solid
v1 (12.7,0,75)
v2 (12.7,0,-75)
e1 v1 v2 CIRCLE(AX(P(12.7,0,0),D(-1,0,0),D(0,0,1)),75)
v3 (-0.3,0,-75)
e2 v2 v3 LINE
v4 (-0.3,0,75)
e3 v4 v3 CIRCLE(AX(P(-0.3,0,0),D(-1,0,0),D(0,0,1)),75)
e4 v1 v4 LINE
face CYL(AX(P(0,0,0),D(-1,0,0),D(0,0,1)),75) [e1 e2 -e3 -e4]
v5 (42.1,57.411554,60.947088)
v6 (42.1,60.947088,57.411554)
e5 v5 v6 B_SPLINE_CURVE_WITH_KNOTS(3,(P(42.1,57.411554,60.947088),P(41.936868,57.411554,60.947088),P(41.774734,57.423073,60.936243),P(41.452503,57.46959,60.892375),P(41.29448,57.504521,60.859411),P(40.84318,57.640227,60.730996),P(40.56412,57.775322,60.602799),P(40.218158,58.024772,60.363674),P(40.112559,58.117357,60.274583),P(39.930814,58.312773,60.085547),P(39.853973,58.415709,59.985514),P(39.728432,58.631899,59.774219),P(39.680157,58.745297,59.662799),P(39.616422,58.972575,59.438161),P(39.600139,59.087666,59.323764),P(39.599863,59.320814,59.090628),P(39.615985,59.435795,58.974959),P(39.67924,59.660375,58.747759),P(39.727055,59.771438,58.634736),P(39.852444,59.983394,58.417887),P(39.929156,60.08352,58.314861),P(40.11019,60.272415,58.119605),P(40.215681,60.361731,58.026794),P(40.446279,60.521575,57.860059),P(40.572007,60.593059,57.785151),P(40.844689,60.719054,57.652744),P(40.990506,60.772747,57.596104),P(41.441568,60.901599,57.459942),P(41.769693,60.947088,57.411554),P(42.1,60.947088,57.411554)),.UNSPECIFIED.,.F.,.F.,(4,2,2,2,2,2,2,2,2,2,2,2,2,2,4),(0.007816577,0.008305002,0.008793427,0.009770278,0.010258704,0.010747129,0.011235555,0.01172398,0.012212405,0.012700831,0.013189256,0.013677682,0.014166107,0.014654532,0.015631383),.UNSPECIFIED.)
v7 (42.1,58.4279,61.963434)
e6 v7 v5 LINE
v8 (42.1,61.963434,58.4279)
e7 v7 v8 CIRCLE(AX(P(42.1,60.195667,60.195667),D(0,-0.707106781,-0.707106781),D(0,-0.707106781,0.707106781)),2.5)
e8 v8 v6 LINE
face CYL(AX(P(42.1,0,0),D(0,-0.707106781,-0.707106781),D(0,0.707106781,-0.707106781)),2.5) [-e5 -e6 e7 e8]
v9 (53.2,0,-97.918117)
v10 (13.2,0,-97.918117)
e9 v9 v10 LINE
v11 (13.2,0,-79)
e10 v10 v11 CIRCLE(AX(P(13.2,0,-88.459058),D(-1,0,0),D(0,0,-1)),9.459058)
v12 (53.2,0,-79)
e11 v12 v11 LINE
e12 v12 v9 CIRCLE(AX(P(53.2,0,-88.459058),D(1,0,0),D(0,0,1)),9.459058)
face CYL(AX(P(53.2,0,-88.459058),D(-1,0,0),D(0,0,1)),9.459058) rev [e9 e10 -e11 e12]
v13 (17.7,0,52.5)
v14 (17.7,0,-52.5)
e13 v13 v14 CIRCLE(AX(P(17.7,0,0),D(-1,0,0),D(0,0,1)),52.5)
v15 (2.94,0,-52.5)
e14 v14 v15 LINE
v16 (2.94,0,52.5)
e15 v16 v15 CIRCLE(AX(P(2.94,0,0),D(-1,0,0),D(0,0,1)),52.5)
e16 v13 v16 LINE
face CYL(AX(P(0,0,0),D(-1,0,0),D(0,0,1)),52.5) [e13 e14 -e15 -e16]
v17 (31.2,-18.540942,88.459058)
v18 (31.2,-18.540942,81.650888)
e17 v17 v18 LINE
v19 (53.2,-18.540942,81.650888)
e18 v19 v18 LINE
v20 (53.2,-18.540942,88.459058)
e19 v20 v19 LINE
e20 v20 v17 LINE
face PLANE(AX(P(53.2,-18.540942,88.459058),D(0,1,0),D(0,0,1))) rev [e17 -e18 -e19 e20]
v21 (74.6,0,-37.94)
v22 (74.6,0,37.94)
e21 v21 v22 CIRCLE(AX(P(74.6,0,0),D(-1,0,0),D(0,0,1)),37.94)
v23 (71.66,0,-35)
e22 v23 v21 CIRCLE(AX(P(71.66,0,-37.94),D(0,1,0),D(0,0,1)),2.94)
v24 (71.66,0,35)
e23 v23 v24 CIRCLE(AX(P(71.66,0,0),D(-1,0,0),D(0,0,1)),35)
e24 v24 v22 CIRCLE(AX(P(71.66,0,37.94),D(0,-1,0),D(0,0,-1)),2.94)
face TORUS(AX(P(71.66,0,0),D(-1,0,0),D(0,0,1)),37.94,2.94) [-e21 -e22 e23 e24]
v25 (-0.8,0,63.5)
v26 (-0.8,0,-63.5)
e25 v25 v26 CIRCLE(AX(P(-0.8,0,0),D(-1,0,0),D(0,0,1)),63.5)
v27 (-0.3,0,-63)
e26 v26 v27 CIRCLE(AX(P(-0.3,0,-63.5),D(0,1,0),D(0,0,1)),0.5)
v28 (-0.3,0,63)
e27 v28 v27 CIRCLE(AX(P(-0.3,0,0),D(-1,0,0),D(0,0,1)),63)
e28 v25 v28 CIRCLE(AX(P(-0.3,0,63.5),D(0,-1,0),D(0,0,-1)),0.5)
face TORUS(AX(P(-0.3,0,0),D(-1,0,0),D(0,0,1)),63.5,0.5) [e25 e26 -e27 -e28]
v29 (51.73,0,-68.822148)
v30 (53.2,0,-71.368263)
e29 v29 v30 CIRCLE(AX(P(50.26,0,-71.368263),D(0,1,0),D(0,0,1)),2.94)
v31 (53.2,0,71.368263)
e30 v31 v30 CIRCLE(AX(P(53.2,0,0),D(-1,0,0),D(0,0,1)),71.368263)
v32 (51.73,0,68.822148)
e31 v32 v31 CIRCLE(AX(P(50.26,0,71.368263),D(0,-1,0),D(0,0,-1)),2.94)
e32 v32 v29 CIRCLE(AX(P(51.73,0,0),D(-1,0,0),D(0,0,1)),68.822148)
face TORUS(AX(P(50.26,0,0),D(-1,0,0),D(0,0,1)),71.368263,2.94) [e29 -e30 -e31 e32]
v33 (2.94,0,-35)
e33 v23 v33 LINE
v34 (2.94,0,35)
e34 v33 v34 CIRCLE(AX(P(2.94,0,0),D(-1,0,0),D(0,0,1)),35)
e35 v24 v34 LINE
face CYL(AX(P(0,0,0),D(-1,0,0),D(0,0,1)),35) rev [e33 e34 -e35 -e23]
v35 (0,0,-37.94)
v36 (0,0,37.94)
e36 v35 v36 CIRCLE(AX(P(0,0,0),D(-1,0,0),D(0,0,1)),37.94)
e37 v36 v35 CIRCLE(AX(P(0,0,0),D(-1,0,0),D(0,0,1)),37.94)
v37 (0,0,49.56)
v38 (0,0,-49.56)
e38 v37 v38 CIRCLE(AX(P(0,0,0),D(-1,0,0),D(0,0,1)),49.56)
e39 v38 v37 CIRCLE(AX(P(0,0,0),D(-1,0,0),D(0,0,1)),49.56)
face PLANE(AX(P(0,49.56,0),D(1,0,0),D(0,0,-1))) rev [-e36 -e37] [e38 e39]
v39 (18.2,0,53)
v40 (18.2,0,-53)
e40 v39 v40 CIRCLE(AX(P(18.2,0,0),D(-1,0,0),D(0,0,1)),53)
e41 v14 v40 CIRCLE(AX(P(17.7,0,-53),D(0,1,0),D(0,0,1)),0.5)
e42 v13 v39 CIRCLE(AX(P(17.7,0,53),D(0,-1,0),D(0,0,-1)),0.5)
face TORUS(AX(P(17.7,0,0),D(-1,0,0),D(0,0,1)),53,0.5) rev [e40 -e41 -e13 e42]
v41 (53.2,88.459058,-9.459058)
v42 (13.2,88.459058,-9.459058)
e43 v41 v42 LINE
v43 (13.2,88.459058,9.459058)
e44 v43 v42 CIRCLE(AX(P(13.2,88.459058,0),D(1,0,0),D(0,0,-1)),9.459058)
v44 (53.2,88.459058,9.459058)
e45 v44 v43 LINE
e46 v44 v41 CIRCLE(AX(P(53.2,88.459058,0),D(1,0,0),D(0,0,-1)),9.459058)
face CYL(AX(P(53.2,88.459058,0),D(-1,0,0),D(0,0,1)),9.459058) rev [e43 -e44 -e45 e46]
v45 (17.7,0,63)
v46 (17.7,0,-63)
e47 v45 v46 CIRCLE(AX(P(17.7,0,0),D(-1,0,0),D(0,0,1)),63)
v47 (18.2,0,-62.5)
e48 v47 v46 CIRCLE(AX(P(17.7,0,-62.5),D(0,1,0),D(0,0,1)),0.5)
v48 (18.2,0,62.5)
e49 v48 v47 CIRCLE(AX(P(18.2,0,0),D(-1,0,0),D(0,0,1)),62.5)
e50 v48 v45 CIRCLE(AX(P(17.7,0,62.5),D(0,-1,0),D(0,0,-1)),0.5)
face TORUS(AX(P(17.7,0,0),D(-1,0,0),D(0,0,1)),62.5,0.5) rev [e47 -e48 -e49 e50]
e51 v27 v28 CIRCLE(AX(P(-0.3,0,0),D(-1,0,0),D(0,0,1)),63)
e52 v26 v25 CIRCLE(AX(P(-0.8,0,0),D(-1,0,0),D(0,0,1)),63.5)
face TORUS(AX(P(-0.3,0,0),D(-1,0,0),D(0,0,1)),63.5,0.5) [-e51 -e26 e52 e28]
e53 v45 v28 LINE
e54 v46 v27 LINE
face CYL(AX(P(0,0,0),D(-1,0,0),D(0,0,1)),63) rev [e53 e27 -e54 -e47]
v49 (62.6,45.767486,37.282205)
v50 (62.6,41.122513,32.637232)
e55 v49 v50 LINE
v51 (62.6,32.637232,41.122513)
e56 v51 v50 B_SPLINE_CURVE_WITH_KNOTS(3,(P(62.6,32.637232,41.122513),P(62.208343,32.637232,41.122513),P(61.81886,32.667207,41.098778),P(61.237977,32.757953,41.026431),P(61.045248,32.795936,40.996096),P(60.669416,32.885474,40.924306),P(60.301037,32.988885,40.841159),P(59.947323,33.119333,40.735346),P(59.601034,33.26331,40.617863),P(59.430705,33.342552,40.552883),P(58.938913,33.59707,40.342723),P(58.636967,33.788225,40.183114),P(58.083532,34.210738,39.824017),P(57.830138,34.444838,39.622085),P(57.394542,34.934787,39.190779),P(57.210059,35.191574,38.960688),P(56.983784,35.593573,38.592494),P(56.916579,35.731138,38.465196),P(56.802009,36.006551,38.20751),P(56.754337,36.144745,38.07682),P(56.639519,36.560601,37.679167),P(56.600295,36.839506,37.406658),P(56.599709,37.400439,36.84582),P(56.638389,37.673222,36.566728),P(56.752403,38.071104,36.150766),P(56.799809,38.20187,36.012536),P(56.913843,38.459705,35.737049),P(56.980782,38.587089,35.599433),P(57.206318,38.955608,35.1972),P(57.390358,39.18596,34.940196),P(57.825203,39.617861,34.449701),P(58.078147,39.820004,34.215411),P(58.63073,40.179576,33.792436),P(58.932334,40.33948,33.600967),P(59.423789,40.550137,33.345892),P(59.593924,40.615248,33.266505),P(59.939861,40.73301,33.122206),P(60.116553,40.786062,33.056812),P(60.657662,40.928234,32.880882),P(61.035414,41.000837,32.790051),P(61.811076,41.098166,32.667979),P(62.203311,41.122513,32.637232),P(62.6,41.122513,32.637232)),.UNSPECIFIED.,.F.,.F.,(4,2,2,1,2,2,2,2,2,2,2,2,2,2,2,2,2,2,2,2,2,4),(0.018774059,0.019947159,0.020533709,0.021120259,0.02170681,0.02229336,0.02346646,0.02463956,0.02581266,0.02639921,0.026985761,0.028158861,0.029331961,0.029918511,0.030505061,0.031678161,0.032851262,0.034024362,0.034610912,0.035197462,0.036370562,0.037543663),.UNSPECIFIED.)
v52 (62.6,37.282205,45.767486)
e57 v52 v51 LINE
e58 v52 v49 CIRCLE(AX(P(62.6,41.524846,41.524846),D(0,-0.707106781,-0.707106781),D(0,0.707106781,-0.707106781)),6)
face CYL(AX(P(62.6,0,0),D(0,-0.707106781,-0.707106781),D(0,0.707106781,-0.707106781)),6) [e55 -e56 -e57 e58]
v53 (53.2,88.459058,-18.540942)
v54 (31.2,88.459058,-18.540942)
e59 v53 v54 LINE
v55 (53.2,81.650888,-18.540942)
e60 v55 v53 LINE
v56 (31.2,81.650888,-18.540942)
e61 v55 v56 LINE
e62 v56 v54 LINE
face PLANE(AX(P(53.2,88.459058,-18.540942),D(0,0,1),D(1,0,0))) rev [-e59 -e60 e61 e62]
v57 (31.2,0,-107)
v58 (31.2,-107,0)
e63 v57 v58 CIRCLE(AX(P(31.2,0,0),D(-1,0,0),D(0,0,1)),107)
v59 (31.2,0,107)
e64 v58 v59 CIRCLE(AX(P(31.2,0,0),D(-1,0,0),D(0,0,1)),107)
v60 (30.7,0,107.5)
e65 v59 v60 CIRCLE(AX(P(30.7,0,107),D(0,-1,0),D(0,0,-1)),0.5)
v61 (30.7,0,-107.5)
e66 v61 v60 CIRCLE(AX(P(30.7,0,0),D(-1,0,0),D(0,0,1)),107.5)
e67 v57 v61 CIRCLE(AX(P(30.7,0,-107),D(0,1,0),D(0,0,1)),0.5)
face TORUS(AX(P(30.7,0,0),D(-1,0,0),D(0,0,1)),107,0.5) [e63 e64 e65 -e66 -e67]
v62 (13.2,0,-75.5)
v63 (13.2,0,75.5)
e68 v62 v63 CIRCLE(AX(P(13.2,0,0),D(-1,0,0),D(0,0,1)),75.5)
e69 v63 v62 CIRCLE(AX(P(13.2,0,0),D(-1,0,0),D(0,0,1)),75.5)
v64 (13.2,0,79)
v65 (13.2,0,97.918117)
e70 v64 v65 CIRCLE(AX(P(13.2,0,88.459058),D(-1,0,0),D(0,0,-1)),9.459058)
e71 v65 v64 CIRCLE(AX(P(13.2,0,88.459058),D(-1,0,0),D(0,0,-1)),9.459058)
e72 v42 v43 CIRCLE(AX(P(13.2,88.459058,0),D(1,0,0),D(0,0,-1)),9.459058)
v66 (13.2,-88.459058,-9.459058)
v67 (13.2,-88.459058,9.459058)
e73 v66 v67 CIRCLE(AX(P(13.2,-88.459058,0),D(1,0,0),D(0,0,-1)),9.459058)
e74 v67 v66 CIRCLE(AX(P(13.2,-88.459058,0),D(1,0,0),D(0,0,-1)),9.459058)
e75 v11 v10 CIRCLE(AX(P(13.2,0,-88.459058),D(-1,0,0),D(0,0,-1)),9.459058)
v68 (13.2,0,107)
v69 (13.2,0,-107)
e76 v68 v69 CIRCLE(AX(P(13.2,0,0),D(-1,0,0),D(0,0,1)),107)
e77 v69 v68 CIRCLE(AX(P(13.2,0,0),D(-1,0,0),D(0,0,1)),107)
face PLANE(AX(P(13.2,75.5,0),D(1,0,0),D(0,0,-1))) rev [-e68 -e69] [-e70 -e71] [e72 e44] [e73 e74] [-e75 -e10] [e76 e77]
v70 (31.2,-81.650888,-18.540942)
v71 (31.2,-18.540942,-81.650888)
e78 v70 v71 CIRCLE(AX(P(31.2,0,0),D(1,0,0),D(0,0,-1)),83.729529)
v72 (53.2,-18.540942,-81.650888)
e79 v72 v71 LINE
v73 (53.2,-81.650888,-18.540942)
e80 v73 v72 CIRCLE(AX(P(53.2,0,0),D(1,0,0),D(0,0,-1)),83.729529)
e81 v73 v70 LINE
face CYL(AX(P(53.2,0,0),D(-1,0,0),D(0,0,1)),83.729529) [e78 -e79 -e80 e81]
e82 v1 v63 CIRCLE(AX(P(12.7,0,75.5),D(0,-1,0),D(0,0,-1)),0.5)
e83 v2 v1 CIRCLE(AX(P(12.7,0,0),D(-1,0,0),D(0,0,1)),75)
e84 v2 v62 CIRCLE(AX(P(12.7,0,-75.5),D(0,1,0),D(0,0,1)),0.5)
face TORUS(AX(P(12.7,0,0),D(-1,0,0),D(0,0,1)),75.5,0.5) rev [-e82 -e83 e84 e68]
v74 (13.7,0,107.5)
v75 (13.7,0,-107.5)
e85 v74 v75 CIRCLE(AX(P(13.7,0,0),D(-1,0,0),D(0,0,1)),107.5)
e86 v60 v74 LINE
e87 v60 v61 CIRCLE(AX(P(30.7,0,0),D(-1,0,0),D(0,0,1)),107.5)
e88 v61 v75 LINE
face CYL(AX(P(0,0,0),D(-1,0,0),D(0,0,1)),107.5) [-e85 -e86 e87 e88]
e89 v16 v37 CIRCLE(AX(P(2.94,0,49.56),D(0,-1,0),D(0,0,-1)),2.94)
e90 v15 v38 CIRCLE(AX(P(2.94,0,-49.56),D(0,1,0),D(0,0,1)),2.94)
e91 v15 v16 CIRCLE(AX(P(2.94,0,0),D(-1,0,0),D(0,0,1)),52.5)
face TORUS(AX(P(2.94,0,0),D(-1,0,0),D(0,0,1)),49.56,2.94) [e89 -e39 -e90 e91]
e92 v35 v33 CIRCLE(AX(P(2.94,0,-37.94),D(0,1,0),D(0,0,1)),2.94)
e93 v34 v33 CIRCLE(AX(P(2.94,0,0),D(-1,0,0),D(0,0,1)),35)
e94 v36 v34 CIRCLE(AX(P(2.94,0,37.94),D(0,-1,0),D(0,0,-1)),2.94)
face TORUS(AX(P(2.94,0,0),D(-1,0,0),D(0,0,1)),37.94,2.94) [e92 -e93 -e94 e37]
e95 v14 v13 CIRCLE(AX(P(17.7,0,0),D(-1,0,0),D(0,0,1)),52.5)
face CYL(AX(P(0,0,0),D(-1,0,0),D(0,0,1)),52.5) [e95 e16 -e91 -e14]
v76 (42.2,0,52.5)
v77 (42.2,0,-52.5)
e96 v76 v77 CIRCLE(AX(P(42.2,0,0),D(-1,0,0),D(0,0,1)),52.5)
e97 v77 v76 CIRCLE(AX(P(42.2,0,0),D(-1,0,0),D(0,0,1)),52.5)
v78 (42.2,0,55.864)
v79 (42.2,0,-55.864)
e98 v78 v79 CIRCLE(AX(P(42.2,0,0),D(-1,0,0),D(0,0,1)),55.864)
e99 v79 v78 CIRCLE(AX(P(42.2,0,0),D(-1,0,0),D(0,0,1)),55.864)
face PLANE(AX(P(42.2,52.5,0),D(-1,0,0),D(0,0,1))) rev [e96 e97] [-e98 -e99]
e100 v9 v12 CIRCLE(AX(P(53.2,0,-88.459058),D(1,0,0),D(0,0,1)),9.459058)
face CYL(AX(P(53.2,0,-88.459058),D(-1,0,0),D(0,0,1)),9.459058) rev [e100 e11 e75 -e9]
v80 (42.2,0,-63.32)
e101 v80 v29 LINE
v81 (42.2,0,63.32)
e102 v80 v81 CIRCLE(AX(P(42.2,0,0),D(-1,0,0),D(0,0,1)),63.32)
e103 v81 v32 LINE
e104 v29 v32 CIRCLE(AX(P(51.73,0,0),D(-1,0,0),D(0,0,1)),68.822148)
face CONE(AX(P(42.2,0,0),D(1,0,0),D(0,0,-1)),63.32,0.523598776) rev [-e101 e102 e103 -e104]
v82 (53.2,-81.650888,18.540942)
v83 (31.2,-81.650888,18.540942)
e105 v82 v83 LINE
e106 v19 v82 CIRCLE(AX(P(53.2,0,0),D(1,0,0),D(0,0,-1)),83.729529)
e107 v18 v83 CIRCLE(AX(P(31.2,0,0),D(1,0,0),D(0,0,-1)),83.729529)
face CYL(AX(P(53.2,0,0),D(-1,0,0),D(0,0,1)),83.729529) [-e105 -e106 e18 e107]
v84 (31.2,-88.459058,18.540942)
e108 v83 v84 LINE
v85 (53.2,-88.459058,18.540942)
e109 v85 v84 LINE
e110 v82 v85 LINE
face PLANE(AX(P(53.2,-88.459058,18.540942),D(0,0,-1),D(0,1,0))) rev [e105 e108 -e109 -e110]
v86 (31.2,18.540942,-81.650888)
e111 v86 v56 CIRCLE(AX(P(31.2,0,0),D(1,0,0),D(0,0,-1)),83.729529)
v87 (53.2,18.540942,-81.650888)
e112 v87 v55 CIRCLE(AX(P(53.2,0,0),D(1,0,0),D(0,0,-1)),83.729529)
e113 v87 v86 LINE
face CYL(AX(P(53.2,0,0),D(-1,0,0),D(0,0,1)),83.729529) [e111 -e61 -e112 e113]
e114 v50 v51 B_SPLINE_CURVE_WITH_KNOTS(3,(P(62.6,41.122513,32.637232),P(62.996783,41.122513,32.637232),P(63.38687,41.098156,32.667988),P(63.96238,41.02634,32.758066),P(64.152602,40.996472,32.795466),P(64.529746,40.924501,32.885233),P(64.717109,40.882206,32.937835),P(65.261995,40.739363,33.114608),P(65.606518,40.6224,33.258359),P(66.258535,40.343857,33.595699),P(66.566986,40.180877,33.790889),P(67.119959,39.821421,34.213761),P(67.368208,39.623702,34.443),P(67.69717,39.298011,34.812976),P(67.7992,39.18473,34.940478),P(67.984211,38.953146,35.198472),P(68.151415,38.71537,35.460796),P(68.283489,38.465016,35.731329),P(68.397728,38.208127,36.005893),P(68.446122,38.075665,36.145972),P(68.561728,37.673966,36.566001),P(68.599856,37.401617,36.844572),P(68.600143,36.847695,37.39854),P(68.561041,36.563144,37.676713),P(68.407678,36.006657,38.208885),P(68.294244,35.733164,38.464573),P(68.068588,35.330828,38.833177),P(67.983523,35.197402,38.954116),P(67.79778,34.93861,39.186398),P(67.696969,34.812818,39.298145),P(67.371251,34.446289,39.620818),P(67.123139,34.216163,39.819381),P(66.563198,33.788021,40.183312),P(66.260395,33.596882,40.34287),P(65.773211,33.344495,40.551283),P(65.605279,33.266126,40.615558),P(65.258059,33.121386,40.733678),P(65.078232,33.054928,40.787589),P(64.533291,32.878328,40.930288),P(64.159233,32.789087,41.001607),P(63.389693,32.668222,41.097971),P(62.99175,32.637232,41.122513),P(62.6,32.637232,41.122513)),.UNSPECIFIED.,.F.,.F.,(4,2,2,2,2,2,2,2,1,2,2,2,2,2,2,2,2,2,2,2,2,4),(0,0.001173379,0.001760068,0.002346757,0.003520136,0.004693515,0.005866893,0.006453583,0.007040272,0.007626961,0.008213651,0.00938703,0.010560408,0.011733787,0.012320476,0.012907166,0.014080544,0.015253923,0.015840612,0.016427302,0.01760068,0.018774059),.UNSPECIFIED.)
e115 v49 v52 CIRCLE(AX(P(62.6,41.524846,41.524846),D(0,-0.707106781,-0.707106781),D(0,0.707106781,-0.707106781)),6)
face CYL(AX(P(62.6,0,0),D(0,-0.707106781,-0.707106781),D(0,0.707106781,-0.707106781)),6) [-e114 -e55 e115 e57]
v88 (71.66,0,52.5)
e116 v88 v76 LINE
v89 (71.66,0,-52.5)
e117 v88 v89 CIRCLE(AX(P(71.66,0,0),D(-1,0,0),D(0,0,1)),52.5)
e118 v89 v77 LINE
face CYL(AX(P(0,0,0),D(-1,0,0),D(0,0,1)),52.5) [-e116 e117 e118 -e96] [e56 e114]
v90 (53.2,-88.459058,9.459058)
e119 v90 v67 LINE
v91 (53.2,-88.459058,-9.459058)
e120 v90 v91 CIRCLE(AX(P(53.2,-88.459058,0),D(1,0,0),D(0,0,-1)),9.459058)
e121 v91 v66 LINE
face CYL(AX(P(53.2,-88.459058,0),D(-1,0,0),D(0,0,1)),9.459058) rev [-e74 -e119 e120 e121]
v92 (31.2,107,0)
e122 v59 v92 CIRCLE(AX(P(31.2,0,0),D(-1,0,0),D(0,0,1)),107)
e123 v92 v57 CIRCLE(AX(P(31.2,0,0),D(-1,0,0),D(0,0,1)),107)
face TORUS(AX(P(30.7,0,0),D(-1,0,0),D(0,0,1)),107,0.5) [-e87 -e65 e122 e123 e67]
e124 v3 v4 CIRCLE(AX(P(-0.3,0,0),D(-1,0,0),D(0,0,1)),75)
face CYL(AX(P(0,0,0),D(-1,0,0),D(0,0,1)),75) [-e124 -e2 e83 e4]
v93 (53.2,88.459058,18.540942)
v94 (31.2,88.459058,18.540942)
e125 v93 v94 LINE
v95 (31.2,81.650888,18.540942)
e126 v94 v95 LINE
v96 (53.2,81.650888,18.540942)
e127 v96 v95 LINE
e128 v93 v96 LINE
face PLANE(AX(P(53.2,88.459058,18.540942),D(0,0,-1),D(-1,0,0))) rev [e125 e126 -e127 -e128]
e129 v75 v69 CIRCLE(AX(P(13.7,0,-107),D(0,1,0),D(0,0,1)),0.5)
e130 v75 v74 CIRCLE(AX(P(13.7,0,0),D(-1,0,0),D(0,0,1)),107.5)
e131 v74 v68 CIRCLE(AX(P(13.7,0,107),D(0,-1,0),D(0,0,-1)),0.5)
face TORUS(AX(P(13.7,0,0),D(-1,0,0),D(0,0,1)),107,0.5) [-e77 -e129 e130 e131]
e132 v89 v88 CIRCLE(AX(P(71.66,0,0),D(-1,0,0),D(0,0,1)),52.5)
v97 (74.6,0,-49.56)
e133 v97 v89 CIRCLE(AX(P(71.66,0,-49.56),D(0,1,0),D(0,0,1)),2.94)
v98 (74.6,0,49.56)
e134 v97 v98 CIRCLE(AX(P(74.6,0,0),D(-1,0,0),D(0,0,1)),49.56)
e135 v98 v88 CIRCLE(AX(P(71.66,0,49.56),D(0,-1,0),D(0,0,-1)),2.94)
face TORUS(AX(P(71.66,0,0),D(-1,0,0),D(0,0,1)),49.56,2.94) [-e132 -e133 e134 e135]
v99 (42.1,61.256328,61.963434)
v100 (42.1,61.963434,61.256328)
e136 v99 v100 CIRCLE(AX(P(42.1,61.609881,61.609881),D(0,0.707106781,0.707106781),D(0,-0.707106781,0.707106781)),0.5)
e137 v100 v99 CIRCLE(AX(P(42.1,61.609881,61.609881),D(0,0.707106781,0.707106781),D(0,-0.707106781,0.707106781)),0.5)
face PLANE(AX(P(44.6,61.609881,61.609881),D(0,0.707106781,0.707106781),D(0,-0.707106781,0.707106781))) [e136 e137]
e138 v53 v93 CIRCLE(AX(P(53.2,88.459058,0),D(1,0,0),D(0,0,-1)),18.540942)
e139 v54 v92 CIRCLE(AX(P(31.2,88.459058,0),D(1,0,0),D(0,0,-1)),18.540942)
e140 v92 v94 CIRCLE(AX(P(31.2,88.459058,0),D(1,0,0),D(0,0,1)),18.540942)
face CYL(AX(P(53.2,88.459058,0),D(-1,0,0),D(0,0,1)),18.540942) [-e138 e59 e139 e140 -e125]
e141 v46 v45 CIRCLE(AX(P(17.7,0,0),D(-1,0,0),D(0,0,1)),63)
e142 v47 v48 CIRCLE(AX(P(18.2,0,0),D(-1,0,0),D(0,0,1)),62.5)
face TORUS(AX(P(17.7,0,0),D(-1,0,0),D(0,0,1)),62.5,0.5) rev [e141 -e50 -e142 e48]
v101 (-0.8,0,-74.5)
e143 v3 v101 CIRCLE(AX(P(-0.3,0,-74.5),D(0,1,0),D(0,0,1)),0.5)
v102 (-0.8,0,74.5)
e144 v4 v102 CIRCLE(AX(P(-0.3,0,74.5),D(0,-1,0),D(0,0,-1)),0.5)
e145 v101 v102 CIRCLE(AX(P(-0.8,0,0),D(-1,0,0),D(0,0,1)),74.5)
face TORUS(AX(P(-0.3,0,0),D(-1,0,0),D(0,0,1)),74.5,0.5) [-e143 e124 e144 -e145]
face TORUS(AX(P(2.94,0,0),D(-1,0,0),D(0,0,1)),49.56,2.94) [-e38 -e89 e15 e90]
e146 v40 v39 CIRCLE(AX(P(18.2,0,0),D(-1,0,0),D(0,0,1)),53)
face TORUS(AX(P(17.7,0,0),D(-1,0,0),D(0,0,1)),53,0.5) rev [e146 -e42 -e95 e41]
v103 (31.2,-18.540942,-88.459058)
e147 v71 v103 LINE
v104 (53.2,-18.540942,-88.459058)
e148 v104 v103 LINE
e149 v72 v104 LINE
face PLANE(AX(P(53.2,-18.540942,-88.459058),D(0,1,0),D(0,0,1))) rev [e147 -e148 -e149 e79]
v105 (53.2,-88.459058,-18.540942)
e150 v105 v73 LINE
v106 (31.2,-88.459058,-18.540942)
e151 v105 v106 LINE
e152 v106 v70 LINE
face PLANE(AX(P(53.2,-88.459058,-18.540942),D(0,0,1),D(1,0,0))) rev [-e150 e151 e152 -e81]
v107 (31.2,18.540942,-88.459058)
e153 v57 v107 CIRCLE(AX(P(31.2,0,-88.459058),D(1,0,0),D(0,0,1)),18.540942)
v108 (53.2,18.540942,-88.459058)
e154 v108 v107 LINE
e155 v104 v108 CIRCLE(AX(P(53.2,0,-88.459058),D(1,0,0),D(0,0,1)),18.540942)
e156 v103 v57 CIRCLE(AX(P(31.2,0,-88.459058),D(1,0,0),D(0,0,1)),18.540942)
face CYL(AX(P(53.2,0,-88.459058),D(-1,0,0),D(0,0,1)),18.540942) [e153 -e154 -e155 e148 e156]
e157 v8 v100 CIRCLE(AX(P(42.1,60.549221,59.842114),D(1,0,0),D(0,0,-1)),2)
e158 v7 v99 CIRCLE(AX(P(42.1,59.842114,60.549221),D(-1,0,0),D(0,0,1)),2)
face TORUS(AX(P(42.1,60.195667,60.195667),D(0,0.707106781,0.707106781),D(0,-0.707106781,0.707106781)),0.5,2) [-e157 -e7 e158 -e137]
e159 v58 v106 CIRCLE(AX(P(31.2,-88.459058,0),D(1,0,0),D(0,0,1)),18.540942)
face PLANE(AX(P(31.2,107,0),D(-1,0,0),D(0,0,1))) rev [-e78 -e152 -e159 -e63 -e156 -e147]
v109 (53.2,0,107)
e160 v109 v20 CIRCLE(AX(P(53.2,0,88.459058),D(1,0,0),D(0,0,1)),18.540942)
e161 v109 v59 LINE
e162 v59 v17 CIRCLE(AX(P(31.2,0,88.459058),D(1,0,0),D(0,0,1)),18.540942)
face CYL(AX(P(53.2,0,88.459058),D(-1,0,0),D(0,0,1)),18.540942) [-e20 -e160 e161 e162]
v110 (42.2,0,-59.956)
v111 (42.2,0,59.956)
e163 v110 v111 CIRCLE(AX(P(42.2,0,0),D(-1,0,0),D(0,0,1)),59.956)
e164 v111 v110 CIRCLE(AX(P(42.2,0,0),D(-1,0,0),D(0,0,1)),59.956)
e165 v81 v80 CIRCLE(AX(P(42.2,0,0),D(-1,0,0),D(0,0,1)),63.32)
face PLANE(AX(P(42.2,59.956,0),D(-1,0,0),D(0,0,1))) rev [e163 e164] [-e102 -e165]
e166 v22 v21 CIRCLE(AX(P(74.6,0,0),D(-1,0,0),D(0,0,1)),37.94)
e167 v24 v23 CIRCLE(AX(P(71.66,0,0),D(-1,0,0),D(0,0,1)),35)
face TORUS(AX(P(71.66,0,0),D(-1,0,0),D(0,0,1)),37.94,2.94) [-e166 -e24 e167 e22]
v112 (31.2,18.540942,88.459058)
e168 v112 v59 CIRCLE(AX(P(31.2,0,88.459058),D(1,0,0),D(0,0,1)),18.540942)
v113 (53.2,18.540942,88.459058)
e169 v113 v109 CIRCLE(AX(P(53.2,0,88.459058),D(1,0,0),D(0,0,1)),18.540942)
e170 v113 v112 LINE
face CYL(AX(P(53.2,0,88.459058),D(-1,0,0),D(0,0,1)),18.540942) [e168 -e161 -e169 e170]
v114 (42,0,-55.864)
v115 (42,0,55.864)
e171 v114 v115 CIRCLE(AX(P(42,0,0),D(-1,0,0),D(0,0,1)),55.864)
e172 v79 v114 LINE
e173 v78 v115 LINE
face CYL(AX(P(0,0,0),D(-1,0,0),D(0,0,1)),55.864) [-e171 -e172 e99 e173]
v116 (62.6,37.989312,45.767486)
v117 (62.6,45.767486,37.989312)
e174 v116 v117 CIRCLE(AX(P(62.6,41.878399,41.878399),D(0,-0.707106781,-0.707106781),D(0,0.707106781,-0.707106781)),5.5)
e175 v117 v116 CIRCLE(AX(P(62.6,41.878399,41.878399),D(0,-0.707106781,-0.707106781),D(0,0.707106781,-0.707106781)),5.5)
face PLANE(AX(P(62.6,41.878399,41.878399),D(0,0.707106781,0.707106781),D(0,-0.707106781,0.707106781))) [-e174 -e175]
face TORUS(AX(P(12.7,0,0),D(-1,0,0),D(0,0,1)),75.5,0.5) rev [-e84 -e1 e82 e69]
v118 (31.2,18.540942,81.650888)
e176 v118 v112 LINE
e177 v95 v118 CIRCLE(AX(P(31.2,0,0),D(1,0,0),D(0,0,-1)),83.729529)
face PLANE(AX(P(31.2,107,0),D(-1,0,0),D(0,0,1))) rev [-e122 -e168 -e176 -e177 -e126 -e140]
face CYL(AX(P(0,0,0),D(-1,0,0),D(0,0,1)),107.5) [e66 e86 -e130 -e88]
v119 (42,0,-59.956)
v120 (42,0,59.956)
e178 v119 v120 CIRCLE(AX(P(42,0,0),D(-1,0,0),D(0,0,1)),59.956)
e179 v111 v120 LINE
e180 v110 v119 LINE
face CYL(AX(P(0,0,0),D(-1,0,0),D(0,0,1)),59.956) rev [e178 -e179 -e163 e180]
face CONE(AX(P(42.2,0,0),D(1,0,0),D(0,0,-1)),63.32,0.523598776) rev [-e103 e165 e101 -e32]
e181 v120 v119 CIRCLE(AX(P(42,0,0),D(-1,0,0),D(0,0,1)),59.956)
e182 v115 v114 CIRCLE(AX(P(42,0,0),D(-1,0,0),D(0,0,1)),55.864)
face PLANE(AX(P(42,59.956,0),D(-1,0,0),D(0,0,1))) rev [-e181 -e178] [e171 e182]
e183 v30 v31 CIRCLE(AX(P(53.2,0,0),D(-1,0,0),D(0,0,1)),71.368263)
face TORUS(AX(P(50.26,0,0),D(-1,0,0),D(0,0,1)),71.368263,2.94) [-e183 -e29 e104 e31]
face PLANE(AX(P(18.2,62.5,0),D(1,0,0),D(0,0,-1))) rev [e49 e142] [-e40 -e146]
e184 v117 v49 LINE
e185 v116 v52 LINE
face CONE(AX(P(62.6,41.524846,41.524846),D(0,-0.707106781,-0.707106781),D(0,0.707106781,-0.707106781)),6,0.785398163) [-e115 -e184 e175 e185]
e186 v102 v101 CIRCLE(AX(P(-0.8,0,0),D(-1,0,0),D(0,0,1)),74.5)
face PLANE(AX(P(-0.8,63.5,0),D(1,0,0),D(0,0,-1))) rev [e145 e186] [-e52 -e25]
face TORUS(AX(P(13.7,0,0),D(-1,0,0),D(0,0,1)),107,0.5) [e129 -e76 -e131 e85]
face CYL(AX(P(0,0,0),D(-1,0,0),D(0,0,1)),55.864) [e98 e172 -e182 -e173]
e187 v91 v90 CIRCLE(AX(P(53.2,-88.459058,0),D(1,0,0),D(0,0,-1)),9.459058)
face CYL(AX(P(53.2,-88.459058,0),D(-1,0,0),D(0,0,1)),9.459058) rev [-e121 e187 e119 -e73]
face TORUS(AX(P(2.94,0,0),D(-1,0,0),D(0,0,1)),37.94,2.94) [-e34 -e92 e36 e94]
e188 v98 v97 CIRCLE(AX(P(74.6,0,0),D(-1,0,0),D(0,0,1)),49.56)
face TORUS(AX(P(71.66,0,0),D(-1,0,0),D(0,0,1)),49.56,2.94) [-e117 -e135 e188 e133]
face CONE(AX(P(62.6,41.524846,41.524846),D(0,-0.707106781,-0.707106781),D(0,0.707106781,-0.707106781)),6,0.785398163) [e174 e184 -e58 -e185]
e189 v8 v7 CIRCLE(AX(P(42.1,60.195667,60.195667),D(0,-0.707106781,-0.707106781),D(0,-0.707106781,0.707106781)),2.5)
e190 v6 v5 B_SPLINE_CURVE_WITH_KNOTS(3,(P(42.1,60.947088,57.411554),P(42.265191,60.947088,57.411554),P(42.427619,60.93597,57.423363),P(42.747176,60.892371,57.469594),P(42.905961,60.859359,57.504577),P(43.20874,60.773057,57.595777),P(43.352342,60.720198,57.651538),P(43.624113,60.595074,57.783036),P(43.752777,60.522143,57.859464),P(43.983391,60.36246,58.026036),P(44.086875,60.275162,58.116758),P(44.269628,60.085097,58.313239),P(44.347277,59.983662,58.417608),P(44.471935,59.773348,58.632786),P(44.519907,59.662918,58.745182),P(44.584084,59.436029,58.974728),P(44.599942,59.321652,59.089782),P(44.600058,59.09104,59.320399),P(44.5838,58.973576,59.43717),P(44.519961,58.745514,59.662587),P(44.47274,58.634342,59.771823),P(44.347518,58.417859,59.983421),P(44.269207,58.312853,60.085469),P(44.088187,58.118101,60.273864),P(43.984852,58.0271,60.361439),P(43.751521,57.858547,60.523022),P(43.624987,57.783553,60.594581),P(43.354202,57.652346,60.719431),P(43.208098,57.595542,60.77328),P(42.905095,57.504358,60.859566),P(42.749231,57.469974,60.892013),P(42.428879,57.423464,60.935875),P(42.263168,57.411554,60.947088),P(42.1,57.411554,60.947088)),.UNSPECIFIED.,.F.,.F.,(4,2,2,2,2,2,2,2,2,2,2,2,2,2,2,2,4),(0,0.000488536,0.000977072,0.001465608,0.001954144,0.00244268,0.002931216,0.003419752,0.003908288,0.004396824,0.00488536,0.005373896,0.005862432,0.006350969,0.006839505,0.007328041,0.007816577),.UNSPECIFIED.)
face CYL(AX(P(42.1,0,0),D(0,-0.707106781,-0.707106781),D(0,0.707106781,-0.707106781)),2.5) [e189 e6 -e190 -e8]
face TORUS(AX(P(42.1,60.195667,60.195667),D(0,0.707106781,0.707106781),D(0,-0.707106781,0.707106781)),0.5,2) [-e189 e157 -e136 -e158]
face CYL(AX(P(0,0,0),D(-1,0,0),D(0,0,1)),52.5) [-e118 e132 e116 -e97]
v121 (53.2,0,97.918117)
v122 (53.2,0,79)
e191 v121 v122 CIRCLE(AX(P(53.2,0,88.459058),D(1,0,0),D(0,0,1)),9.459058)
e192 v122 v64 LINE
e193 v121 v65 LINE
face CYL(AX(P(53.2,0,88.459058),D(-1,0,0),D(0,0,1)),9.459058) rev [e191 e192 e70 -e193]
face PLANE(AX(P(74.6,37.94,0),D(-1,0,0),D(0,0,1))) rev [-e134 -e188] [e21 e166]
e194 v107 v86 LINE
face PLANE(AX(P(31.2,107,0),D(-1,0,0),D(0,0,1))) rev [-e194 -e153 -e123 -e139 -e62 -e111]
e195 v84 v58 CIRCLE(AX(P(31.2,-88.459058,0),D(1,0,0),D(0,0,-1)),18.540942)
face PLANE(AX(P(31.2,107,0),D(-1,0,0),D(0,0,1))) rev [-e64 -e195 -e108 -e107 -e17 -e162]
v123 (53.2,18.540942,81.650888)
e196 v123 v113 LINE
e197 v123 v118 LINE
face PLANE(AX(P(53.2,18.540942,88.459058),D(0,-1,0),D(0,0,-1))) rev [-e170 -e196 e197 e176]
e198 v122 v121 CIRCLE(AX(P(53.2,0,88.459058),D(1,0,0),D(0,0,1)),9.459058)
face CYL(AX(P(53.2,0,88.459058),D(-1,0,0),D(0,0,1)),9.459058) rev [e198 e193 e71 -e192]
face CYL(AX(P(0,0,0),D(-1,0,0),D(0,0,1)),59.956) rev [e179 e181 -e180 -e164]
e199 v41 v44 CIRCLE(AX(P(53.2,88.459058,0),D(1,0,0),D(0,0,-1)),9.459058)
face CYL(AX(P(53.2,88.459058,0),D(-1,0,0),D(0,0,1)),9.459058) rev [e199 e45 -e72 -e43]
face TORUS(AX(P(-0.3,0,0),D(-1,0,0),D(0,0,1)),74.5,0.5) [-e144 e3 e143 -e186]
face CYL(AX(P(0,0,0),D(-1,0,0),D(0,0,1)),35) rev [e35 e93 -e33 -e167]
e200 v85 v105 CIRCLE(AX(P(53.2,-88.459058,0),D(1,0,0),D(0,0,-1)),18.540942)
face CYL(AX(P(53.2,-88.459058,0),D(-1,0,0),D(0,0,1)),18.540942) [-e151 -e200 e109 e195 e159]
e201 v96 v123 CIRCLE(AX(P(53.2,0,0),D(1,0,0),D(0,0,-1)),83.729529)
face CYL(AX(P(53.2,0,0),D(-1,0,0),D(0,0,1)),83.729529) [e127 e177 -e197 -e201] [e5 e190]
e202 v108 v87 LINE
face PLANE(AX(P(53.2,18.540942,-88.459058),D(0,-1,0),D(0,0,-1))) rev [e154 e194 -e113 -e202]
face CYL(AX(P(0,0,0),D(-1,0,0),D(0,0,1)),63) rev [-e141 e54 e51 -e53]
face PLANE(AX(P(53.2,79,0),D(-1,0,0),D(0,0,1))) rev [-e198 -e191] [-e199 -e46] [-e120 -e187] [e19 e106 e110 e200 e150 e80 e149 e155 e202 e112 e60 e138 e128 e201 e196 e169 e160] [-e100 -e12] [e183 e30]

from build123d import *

# Parameters (mm, degrees)
SKETCH_2_2_R        = 9.459058326
SKETCH_2_2_R_2      = 71.368262753
BOSS_EXTRUDE1_DEPTH = 22
CUT_EXTRUDE1_START  = -18
SKETCH_2_2_2_R      = 9.459058326
CUT_EXTRUDE1_DEPTH  = 18
SKETCH3_W           = 2.5
SKETCH3_H           = 5.4
FILLET2_R           = 2


with BuildPart() as part:
    # Sketch1 → Revolve1 (revolve)
    with BuildSketch(Plane.XY, mode=Mode.PRIVATE) as revolve1_sk:
        with BuildLine():
            Line((-0.3, 63), (17.7, 63))
            ThreePointArc((17.7, 63), (18.053553391, 62.853553391), (18.2, 62.5))
            Line((18.2, 62.5), (18.2, 53))
            ThreePointArc((18.2, 53), (18.053553391, 52.646446609), (17.7, 52.5))
            Line((17.7, 52.5), (2.94, 52.5))
            ThreePointArc((2.94, 52.5), (0.861106063, 51.638893937), (0, 49.56))
            Line((0, 49.56), (0, 37.94))
            ThreePointArc((0, 37.94), (0.861106063, 35.861106063), (2.94, 35))
            Line((2.94, 35), (71.66, 35))
            ThreePointArc((71.66, 35), (73.738893937, 35.861106063), (74.6, 37.94))
            Line((74.6, 37.94), (74.6, 49.56))
            ThreePointArc((74.6, 49.56), (73.738893937, 51.638893937), (71.66, 52.5))
            Line((71.66, 52.5), (42.2, 52.5))
            Line((42.2, 52.5), (42.2, 55.864))
            Line((42.2, 55.864), (42, 55.864))
            Line((42, 55.864), (42, 59.956))
            Line((42, 59.956), (42.2, 59.956))
            Line((42.2, 59.956), (42.2, 63.32))
            Line((42.2, 63.32), (51.73, 68.822148065))
            ThreePointArc((51.73, 68.822148065), (52.806114687, 69.898262753), (53.2, 71.368262753))
            Line((53.2, 71.368262753), (53.2, 79))
            Line((53.2, 79), (31.2, 79))
            Line((31.2, 79), (31.2, 107))
            ThreePointArc((31.2, 107), (31.053553391, 107.353553391), (30.7, 107.5))
            Line((30.7, 107.5), (13.7, 107.5))
            ThreePointArc((13.7, 107.5), (13.346446609, 107.353553391), (13.2, 107))
            Line((13.2, 107), (13.2, 75.5))
            ThreePointArc((13.2, 75.5), (13.053553391, 75.146446609), (12.7, 75))
            Line((12.7, 75), (-0.3, 75))
            ThreePointArc((-0.3, 75), (-0.653553391, 74.853553391), (-0.8, 74.5))
            Line((-0.8, 74.5), (-0.8, 63.5))
            ThreePointArc((-0.8, 63.5), (-0.653553391, 63.146446609), (-0.3, 63))
        make_face()
    revolve(revolve1_sk.sketch.rotate(Axis((0, 0, 0), (1, 0, 0)), 90), axis=Axis((0, 0, 0), (1, 0, 0)))

    # Sketch 2_2 → Boss-Extrude1 (add)
    with BuildSketch(Plane(origin=(31.2, 0, 0), x_dir=(0, 0, -1), z_dir=(1, 0, 0))):
        with BuildLine():
            Line((-18.540941674, 88.459058326), (-18.540941674, 81.65088815))
            ThreePointArc((-18.540941674, 81.65088815), (-59.205717857, 59.205717857), (-81.65088815, 18.540941674))
            Line((-81.65088815, 18.540941674), (-88.459058326, 18.540941674))
            ThreePointArc((-88.459058326, 18.540941674), (-107, 0), (-88.459058326, -18.540941674))
            Line((-88.459058326, -18.540941674), (-81.65088815, -18.540941674))
            ThreePointArc((-81.65088815, -18.540941674), (-59.205717857, -59.205717857), (-18.540941674, -81.65088815))
            Line((-18.540941674, -81.65088815), (-18.540941674, -88.459058326))
            ThreePointArc((-18.540941674, -88.459058326), (0, -107), (18.540941674, -88.459058326))
            Line((18.540941674, -88.459058326), (18.540941674, -81.65088815))
            ThreePointArc((18.540941674, -81.65088815), (59.205717857, -59.205717857), (81.65088815, -18.540941674))
            Line((81.65088815, -18.540941674), (88.459058326, -18.540941674))
            ThreePointArc((88.459058326, -18.540941674), (107, 0), (88.459058326, 18.540941674))
            Line((88.459058326, 18.540941674), (81.65088815, 18.540941674))
            ThreePointArc((81.65088815, 18.540941674), (59.205717857, 59.205717857), (18.540941674, 81.65088815))
            Line((18.540941674, 81.65088815), (18.540941674, 88.459058326))
            ThreePointArc((18.540941674, 88.459058326), (0, 107), (-18.540941674, 88.459058326))
        make_face()
        with Locations((0, 88.459058326)):
            Circle(SKETCH_2_2_R, mode=Mode.SUBTRACT)
        with Locations(Location((88.459058326, 0, 0), (0, 0, 180))):
            Circle(SKETCH_2_2_R, mode=Mode.SUBTRACT)
        with Locations((0, -88.459058326)):
            Circle(SKETCH_2_2_R, mode=Mode.SUBTRACT)
        with Locations(Location((-88.459058326, 0, 0), (0, 0, 180))):
            Circle(SKETCH_2_2_R, mode=Mode.SUBTRACT)
        Circle(SKETCH_2_2_R_2, mode=Mode.SUBTRACT)
    extrude(amount=BOSS_EXTRUDE1_DEPTH)

    # Sketch 2_2 2 → Cut-Extrude1 (cut)
    with BuildSketch(Plane(origin=(31.2, 0, 0), x_dir=(0, 0, -1), z_dir=(1, 0, 0)).offset(CUT_EXTRUDE1_START)):
        with Locations((0, 88.459058326)):
            Circle(SKETCH_2_2_2_R)
        with Locations(Location((88.459058326, 0, 0), (0, 0, 180))):
            Circle(SKETCH_2_2_2_R)
        with Locations((0, -88.459058326)):
            Circle(SKETCH_2_2_2_R)
        with Locations(Location((-88.459058326, 0, 0), (0, 0, 180))):
            Circle(SKETCH_2_2_2_R)
    extrude(amount=CUT_EXTRUDE1_DEPTH, mode=Mode.SUBTRACT)

    # Sketch3 → Revolve2 (revolve)
    with BuildSketch(Plane(origin=(0, 0, 0), x_dir=(1, 0, 0), z_dir=(0, -0.7071067811865475, 0.7071067811865477)), mode=Mode.PRIVATE) as revolve2_sk:
        with Locations((43.35, 84.429529163)):
            Rectangle(SKETCH3_W, SKETCH3_H)
    revolve(revolve2_sk.sketch.rotate(Axis((42.1, 0, 0), (0, 0.7071067811865477, 0.7071067811865475)), 90), axis=Axis((42.1, 0, 0), (0, 0.7071067811865477, 0.7071067811865475)))

    # Sketch4 → Revolve3 (revolve)
    with BuildSketch(Plane(origin=(0, 0, 0), x_dir=(1, 0, 0), z_dir=(0, -0.7071067811865475, 0.7071067811865477)), mode=Mode.PRIVATE) as revolve3_sk:
        Polygon((62.6, 51.5), (62.6, 59.225), (68.1, 59.225), (68.6, 58.725), (68.6, 51.5), align=None)
    revolve(revolve3_sk.sketch.rotate(Axis((62.6, 0, 0), (0, 0.7071067811865476, 0.7071067811865475)), 90), axis=Axis((62.6, 0, 0), (0, 0.7071067811865476, 0.7071067811865475)))

    # Fillet2
    fillet2_edges = [part.edges().sort_by_distance(p)[0] for p in [
        (42.1, 59.84211396, 63.377647866),
    ]]
    fillet(fillet2_edges, radius=FILLET2_R)


solid = part.part
